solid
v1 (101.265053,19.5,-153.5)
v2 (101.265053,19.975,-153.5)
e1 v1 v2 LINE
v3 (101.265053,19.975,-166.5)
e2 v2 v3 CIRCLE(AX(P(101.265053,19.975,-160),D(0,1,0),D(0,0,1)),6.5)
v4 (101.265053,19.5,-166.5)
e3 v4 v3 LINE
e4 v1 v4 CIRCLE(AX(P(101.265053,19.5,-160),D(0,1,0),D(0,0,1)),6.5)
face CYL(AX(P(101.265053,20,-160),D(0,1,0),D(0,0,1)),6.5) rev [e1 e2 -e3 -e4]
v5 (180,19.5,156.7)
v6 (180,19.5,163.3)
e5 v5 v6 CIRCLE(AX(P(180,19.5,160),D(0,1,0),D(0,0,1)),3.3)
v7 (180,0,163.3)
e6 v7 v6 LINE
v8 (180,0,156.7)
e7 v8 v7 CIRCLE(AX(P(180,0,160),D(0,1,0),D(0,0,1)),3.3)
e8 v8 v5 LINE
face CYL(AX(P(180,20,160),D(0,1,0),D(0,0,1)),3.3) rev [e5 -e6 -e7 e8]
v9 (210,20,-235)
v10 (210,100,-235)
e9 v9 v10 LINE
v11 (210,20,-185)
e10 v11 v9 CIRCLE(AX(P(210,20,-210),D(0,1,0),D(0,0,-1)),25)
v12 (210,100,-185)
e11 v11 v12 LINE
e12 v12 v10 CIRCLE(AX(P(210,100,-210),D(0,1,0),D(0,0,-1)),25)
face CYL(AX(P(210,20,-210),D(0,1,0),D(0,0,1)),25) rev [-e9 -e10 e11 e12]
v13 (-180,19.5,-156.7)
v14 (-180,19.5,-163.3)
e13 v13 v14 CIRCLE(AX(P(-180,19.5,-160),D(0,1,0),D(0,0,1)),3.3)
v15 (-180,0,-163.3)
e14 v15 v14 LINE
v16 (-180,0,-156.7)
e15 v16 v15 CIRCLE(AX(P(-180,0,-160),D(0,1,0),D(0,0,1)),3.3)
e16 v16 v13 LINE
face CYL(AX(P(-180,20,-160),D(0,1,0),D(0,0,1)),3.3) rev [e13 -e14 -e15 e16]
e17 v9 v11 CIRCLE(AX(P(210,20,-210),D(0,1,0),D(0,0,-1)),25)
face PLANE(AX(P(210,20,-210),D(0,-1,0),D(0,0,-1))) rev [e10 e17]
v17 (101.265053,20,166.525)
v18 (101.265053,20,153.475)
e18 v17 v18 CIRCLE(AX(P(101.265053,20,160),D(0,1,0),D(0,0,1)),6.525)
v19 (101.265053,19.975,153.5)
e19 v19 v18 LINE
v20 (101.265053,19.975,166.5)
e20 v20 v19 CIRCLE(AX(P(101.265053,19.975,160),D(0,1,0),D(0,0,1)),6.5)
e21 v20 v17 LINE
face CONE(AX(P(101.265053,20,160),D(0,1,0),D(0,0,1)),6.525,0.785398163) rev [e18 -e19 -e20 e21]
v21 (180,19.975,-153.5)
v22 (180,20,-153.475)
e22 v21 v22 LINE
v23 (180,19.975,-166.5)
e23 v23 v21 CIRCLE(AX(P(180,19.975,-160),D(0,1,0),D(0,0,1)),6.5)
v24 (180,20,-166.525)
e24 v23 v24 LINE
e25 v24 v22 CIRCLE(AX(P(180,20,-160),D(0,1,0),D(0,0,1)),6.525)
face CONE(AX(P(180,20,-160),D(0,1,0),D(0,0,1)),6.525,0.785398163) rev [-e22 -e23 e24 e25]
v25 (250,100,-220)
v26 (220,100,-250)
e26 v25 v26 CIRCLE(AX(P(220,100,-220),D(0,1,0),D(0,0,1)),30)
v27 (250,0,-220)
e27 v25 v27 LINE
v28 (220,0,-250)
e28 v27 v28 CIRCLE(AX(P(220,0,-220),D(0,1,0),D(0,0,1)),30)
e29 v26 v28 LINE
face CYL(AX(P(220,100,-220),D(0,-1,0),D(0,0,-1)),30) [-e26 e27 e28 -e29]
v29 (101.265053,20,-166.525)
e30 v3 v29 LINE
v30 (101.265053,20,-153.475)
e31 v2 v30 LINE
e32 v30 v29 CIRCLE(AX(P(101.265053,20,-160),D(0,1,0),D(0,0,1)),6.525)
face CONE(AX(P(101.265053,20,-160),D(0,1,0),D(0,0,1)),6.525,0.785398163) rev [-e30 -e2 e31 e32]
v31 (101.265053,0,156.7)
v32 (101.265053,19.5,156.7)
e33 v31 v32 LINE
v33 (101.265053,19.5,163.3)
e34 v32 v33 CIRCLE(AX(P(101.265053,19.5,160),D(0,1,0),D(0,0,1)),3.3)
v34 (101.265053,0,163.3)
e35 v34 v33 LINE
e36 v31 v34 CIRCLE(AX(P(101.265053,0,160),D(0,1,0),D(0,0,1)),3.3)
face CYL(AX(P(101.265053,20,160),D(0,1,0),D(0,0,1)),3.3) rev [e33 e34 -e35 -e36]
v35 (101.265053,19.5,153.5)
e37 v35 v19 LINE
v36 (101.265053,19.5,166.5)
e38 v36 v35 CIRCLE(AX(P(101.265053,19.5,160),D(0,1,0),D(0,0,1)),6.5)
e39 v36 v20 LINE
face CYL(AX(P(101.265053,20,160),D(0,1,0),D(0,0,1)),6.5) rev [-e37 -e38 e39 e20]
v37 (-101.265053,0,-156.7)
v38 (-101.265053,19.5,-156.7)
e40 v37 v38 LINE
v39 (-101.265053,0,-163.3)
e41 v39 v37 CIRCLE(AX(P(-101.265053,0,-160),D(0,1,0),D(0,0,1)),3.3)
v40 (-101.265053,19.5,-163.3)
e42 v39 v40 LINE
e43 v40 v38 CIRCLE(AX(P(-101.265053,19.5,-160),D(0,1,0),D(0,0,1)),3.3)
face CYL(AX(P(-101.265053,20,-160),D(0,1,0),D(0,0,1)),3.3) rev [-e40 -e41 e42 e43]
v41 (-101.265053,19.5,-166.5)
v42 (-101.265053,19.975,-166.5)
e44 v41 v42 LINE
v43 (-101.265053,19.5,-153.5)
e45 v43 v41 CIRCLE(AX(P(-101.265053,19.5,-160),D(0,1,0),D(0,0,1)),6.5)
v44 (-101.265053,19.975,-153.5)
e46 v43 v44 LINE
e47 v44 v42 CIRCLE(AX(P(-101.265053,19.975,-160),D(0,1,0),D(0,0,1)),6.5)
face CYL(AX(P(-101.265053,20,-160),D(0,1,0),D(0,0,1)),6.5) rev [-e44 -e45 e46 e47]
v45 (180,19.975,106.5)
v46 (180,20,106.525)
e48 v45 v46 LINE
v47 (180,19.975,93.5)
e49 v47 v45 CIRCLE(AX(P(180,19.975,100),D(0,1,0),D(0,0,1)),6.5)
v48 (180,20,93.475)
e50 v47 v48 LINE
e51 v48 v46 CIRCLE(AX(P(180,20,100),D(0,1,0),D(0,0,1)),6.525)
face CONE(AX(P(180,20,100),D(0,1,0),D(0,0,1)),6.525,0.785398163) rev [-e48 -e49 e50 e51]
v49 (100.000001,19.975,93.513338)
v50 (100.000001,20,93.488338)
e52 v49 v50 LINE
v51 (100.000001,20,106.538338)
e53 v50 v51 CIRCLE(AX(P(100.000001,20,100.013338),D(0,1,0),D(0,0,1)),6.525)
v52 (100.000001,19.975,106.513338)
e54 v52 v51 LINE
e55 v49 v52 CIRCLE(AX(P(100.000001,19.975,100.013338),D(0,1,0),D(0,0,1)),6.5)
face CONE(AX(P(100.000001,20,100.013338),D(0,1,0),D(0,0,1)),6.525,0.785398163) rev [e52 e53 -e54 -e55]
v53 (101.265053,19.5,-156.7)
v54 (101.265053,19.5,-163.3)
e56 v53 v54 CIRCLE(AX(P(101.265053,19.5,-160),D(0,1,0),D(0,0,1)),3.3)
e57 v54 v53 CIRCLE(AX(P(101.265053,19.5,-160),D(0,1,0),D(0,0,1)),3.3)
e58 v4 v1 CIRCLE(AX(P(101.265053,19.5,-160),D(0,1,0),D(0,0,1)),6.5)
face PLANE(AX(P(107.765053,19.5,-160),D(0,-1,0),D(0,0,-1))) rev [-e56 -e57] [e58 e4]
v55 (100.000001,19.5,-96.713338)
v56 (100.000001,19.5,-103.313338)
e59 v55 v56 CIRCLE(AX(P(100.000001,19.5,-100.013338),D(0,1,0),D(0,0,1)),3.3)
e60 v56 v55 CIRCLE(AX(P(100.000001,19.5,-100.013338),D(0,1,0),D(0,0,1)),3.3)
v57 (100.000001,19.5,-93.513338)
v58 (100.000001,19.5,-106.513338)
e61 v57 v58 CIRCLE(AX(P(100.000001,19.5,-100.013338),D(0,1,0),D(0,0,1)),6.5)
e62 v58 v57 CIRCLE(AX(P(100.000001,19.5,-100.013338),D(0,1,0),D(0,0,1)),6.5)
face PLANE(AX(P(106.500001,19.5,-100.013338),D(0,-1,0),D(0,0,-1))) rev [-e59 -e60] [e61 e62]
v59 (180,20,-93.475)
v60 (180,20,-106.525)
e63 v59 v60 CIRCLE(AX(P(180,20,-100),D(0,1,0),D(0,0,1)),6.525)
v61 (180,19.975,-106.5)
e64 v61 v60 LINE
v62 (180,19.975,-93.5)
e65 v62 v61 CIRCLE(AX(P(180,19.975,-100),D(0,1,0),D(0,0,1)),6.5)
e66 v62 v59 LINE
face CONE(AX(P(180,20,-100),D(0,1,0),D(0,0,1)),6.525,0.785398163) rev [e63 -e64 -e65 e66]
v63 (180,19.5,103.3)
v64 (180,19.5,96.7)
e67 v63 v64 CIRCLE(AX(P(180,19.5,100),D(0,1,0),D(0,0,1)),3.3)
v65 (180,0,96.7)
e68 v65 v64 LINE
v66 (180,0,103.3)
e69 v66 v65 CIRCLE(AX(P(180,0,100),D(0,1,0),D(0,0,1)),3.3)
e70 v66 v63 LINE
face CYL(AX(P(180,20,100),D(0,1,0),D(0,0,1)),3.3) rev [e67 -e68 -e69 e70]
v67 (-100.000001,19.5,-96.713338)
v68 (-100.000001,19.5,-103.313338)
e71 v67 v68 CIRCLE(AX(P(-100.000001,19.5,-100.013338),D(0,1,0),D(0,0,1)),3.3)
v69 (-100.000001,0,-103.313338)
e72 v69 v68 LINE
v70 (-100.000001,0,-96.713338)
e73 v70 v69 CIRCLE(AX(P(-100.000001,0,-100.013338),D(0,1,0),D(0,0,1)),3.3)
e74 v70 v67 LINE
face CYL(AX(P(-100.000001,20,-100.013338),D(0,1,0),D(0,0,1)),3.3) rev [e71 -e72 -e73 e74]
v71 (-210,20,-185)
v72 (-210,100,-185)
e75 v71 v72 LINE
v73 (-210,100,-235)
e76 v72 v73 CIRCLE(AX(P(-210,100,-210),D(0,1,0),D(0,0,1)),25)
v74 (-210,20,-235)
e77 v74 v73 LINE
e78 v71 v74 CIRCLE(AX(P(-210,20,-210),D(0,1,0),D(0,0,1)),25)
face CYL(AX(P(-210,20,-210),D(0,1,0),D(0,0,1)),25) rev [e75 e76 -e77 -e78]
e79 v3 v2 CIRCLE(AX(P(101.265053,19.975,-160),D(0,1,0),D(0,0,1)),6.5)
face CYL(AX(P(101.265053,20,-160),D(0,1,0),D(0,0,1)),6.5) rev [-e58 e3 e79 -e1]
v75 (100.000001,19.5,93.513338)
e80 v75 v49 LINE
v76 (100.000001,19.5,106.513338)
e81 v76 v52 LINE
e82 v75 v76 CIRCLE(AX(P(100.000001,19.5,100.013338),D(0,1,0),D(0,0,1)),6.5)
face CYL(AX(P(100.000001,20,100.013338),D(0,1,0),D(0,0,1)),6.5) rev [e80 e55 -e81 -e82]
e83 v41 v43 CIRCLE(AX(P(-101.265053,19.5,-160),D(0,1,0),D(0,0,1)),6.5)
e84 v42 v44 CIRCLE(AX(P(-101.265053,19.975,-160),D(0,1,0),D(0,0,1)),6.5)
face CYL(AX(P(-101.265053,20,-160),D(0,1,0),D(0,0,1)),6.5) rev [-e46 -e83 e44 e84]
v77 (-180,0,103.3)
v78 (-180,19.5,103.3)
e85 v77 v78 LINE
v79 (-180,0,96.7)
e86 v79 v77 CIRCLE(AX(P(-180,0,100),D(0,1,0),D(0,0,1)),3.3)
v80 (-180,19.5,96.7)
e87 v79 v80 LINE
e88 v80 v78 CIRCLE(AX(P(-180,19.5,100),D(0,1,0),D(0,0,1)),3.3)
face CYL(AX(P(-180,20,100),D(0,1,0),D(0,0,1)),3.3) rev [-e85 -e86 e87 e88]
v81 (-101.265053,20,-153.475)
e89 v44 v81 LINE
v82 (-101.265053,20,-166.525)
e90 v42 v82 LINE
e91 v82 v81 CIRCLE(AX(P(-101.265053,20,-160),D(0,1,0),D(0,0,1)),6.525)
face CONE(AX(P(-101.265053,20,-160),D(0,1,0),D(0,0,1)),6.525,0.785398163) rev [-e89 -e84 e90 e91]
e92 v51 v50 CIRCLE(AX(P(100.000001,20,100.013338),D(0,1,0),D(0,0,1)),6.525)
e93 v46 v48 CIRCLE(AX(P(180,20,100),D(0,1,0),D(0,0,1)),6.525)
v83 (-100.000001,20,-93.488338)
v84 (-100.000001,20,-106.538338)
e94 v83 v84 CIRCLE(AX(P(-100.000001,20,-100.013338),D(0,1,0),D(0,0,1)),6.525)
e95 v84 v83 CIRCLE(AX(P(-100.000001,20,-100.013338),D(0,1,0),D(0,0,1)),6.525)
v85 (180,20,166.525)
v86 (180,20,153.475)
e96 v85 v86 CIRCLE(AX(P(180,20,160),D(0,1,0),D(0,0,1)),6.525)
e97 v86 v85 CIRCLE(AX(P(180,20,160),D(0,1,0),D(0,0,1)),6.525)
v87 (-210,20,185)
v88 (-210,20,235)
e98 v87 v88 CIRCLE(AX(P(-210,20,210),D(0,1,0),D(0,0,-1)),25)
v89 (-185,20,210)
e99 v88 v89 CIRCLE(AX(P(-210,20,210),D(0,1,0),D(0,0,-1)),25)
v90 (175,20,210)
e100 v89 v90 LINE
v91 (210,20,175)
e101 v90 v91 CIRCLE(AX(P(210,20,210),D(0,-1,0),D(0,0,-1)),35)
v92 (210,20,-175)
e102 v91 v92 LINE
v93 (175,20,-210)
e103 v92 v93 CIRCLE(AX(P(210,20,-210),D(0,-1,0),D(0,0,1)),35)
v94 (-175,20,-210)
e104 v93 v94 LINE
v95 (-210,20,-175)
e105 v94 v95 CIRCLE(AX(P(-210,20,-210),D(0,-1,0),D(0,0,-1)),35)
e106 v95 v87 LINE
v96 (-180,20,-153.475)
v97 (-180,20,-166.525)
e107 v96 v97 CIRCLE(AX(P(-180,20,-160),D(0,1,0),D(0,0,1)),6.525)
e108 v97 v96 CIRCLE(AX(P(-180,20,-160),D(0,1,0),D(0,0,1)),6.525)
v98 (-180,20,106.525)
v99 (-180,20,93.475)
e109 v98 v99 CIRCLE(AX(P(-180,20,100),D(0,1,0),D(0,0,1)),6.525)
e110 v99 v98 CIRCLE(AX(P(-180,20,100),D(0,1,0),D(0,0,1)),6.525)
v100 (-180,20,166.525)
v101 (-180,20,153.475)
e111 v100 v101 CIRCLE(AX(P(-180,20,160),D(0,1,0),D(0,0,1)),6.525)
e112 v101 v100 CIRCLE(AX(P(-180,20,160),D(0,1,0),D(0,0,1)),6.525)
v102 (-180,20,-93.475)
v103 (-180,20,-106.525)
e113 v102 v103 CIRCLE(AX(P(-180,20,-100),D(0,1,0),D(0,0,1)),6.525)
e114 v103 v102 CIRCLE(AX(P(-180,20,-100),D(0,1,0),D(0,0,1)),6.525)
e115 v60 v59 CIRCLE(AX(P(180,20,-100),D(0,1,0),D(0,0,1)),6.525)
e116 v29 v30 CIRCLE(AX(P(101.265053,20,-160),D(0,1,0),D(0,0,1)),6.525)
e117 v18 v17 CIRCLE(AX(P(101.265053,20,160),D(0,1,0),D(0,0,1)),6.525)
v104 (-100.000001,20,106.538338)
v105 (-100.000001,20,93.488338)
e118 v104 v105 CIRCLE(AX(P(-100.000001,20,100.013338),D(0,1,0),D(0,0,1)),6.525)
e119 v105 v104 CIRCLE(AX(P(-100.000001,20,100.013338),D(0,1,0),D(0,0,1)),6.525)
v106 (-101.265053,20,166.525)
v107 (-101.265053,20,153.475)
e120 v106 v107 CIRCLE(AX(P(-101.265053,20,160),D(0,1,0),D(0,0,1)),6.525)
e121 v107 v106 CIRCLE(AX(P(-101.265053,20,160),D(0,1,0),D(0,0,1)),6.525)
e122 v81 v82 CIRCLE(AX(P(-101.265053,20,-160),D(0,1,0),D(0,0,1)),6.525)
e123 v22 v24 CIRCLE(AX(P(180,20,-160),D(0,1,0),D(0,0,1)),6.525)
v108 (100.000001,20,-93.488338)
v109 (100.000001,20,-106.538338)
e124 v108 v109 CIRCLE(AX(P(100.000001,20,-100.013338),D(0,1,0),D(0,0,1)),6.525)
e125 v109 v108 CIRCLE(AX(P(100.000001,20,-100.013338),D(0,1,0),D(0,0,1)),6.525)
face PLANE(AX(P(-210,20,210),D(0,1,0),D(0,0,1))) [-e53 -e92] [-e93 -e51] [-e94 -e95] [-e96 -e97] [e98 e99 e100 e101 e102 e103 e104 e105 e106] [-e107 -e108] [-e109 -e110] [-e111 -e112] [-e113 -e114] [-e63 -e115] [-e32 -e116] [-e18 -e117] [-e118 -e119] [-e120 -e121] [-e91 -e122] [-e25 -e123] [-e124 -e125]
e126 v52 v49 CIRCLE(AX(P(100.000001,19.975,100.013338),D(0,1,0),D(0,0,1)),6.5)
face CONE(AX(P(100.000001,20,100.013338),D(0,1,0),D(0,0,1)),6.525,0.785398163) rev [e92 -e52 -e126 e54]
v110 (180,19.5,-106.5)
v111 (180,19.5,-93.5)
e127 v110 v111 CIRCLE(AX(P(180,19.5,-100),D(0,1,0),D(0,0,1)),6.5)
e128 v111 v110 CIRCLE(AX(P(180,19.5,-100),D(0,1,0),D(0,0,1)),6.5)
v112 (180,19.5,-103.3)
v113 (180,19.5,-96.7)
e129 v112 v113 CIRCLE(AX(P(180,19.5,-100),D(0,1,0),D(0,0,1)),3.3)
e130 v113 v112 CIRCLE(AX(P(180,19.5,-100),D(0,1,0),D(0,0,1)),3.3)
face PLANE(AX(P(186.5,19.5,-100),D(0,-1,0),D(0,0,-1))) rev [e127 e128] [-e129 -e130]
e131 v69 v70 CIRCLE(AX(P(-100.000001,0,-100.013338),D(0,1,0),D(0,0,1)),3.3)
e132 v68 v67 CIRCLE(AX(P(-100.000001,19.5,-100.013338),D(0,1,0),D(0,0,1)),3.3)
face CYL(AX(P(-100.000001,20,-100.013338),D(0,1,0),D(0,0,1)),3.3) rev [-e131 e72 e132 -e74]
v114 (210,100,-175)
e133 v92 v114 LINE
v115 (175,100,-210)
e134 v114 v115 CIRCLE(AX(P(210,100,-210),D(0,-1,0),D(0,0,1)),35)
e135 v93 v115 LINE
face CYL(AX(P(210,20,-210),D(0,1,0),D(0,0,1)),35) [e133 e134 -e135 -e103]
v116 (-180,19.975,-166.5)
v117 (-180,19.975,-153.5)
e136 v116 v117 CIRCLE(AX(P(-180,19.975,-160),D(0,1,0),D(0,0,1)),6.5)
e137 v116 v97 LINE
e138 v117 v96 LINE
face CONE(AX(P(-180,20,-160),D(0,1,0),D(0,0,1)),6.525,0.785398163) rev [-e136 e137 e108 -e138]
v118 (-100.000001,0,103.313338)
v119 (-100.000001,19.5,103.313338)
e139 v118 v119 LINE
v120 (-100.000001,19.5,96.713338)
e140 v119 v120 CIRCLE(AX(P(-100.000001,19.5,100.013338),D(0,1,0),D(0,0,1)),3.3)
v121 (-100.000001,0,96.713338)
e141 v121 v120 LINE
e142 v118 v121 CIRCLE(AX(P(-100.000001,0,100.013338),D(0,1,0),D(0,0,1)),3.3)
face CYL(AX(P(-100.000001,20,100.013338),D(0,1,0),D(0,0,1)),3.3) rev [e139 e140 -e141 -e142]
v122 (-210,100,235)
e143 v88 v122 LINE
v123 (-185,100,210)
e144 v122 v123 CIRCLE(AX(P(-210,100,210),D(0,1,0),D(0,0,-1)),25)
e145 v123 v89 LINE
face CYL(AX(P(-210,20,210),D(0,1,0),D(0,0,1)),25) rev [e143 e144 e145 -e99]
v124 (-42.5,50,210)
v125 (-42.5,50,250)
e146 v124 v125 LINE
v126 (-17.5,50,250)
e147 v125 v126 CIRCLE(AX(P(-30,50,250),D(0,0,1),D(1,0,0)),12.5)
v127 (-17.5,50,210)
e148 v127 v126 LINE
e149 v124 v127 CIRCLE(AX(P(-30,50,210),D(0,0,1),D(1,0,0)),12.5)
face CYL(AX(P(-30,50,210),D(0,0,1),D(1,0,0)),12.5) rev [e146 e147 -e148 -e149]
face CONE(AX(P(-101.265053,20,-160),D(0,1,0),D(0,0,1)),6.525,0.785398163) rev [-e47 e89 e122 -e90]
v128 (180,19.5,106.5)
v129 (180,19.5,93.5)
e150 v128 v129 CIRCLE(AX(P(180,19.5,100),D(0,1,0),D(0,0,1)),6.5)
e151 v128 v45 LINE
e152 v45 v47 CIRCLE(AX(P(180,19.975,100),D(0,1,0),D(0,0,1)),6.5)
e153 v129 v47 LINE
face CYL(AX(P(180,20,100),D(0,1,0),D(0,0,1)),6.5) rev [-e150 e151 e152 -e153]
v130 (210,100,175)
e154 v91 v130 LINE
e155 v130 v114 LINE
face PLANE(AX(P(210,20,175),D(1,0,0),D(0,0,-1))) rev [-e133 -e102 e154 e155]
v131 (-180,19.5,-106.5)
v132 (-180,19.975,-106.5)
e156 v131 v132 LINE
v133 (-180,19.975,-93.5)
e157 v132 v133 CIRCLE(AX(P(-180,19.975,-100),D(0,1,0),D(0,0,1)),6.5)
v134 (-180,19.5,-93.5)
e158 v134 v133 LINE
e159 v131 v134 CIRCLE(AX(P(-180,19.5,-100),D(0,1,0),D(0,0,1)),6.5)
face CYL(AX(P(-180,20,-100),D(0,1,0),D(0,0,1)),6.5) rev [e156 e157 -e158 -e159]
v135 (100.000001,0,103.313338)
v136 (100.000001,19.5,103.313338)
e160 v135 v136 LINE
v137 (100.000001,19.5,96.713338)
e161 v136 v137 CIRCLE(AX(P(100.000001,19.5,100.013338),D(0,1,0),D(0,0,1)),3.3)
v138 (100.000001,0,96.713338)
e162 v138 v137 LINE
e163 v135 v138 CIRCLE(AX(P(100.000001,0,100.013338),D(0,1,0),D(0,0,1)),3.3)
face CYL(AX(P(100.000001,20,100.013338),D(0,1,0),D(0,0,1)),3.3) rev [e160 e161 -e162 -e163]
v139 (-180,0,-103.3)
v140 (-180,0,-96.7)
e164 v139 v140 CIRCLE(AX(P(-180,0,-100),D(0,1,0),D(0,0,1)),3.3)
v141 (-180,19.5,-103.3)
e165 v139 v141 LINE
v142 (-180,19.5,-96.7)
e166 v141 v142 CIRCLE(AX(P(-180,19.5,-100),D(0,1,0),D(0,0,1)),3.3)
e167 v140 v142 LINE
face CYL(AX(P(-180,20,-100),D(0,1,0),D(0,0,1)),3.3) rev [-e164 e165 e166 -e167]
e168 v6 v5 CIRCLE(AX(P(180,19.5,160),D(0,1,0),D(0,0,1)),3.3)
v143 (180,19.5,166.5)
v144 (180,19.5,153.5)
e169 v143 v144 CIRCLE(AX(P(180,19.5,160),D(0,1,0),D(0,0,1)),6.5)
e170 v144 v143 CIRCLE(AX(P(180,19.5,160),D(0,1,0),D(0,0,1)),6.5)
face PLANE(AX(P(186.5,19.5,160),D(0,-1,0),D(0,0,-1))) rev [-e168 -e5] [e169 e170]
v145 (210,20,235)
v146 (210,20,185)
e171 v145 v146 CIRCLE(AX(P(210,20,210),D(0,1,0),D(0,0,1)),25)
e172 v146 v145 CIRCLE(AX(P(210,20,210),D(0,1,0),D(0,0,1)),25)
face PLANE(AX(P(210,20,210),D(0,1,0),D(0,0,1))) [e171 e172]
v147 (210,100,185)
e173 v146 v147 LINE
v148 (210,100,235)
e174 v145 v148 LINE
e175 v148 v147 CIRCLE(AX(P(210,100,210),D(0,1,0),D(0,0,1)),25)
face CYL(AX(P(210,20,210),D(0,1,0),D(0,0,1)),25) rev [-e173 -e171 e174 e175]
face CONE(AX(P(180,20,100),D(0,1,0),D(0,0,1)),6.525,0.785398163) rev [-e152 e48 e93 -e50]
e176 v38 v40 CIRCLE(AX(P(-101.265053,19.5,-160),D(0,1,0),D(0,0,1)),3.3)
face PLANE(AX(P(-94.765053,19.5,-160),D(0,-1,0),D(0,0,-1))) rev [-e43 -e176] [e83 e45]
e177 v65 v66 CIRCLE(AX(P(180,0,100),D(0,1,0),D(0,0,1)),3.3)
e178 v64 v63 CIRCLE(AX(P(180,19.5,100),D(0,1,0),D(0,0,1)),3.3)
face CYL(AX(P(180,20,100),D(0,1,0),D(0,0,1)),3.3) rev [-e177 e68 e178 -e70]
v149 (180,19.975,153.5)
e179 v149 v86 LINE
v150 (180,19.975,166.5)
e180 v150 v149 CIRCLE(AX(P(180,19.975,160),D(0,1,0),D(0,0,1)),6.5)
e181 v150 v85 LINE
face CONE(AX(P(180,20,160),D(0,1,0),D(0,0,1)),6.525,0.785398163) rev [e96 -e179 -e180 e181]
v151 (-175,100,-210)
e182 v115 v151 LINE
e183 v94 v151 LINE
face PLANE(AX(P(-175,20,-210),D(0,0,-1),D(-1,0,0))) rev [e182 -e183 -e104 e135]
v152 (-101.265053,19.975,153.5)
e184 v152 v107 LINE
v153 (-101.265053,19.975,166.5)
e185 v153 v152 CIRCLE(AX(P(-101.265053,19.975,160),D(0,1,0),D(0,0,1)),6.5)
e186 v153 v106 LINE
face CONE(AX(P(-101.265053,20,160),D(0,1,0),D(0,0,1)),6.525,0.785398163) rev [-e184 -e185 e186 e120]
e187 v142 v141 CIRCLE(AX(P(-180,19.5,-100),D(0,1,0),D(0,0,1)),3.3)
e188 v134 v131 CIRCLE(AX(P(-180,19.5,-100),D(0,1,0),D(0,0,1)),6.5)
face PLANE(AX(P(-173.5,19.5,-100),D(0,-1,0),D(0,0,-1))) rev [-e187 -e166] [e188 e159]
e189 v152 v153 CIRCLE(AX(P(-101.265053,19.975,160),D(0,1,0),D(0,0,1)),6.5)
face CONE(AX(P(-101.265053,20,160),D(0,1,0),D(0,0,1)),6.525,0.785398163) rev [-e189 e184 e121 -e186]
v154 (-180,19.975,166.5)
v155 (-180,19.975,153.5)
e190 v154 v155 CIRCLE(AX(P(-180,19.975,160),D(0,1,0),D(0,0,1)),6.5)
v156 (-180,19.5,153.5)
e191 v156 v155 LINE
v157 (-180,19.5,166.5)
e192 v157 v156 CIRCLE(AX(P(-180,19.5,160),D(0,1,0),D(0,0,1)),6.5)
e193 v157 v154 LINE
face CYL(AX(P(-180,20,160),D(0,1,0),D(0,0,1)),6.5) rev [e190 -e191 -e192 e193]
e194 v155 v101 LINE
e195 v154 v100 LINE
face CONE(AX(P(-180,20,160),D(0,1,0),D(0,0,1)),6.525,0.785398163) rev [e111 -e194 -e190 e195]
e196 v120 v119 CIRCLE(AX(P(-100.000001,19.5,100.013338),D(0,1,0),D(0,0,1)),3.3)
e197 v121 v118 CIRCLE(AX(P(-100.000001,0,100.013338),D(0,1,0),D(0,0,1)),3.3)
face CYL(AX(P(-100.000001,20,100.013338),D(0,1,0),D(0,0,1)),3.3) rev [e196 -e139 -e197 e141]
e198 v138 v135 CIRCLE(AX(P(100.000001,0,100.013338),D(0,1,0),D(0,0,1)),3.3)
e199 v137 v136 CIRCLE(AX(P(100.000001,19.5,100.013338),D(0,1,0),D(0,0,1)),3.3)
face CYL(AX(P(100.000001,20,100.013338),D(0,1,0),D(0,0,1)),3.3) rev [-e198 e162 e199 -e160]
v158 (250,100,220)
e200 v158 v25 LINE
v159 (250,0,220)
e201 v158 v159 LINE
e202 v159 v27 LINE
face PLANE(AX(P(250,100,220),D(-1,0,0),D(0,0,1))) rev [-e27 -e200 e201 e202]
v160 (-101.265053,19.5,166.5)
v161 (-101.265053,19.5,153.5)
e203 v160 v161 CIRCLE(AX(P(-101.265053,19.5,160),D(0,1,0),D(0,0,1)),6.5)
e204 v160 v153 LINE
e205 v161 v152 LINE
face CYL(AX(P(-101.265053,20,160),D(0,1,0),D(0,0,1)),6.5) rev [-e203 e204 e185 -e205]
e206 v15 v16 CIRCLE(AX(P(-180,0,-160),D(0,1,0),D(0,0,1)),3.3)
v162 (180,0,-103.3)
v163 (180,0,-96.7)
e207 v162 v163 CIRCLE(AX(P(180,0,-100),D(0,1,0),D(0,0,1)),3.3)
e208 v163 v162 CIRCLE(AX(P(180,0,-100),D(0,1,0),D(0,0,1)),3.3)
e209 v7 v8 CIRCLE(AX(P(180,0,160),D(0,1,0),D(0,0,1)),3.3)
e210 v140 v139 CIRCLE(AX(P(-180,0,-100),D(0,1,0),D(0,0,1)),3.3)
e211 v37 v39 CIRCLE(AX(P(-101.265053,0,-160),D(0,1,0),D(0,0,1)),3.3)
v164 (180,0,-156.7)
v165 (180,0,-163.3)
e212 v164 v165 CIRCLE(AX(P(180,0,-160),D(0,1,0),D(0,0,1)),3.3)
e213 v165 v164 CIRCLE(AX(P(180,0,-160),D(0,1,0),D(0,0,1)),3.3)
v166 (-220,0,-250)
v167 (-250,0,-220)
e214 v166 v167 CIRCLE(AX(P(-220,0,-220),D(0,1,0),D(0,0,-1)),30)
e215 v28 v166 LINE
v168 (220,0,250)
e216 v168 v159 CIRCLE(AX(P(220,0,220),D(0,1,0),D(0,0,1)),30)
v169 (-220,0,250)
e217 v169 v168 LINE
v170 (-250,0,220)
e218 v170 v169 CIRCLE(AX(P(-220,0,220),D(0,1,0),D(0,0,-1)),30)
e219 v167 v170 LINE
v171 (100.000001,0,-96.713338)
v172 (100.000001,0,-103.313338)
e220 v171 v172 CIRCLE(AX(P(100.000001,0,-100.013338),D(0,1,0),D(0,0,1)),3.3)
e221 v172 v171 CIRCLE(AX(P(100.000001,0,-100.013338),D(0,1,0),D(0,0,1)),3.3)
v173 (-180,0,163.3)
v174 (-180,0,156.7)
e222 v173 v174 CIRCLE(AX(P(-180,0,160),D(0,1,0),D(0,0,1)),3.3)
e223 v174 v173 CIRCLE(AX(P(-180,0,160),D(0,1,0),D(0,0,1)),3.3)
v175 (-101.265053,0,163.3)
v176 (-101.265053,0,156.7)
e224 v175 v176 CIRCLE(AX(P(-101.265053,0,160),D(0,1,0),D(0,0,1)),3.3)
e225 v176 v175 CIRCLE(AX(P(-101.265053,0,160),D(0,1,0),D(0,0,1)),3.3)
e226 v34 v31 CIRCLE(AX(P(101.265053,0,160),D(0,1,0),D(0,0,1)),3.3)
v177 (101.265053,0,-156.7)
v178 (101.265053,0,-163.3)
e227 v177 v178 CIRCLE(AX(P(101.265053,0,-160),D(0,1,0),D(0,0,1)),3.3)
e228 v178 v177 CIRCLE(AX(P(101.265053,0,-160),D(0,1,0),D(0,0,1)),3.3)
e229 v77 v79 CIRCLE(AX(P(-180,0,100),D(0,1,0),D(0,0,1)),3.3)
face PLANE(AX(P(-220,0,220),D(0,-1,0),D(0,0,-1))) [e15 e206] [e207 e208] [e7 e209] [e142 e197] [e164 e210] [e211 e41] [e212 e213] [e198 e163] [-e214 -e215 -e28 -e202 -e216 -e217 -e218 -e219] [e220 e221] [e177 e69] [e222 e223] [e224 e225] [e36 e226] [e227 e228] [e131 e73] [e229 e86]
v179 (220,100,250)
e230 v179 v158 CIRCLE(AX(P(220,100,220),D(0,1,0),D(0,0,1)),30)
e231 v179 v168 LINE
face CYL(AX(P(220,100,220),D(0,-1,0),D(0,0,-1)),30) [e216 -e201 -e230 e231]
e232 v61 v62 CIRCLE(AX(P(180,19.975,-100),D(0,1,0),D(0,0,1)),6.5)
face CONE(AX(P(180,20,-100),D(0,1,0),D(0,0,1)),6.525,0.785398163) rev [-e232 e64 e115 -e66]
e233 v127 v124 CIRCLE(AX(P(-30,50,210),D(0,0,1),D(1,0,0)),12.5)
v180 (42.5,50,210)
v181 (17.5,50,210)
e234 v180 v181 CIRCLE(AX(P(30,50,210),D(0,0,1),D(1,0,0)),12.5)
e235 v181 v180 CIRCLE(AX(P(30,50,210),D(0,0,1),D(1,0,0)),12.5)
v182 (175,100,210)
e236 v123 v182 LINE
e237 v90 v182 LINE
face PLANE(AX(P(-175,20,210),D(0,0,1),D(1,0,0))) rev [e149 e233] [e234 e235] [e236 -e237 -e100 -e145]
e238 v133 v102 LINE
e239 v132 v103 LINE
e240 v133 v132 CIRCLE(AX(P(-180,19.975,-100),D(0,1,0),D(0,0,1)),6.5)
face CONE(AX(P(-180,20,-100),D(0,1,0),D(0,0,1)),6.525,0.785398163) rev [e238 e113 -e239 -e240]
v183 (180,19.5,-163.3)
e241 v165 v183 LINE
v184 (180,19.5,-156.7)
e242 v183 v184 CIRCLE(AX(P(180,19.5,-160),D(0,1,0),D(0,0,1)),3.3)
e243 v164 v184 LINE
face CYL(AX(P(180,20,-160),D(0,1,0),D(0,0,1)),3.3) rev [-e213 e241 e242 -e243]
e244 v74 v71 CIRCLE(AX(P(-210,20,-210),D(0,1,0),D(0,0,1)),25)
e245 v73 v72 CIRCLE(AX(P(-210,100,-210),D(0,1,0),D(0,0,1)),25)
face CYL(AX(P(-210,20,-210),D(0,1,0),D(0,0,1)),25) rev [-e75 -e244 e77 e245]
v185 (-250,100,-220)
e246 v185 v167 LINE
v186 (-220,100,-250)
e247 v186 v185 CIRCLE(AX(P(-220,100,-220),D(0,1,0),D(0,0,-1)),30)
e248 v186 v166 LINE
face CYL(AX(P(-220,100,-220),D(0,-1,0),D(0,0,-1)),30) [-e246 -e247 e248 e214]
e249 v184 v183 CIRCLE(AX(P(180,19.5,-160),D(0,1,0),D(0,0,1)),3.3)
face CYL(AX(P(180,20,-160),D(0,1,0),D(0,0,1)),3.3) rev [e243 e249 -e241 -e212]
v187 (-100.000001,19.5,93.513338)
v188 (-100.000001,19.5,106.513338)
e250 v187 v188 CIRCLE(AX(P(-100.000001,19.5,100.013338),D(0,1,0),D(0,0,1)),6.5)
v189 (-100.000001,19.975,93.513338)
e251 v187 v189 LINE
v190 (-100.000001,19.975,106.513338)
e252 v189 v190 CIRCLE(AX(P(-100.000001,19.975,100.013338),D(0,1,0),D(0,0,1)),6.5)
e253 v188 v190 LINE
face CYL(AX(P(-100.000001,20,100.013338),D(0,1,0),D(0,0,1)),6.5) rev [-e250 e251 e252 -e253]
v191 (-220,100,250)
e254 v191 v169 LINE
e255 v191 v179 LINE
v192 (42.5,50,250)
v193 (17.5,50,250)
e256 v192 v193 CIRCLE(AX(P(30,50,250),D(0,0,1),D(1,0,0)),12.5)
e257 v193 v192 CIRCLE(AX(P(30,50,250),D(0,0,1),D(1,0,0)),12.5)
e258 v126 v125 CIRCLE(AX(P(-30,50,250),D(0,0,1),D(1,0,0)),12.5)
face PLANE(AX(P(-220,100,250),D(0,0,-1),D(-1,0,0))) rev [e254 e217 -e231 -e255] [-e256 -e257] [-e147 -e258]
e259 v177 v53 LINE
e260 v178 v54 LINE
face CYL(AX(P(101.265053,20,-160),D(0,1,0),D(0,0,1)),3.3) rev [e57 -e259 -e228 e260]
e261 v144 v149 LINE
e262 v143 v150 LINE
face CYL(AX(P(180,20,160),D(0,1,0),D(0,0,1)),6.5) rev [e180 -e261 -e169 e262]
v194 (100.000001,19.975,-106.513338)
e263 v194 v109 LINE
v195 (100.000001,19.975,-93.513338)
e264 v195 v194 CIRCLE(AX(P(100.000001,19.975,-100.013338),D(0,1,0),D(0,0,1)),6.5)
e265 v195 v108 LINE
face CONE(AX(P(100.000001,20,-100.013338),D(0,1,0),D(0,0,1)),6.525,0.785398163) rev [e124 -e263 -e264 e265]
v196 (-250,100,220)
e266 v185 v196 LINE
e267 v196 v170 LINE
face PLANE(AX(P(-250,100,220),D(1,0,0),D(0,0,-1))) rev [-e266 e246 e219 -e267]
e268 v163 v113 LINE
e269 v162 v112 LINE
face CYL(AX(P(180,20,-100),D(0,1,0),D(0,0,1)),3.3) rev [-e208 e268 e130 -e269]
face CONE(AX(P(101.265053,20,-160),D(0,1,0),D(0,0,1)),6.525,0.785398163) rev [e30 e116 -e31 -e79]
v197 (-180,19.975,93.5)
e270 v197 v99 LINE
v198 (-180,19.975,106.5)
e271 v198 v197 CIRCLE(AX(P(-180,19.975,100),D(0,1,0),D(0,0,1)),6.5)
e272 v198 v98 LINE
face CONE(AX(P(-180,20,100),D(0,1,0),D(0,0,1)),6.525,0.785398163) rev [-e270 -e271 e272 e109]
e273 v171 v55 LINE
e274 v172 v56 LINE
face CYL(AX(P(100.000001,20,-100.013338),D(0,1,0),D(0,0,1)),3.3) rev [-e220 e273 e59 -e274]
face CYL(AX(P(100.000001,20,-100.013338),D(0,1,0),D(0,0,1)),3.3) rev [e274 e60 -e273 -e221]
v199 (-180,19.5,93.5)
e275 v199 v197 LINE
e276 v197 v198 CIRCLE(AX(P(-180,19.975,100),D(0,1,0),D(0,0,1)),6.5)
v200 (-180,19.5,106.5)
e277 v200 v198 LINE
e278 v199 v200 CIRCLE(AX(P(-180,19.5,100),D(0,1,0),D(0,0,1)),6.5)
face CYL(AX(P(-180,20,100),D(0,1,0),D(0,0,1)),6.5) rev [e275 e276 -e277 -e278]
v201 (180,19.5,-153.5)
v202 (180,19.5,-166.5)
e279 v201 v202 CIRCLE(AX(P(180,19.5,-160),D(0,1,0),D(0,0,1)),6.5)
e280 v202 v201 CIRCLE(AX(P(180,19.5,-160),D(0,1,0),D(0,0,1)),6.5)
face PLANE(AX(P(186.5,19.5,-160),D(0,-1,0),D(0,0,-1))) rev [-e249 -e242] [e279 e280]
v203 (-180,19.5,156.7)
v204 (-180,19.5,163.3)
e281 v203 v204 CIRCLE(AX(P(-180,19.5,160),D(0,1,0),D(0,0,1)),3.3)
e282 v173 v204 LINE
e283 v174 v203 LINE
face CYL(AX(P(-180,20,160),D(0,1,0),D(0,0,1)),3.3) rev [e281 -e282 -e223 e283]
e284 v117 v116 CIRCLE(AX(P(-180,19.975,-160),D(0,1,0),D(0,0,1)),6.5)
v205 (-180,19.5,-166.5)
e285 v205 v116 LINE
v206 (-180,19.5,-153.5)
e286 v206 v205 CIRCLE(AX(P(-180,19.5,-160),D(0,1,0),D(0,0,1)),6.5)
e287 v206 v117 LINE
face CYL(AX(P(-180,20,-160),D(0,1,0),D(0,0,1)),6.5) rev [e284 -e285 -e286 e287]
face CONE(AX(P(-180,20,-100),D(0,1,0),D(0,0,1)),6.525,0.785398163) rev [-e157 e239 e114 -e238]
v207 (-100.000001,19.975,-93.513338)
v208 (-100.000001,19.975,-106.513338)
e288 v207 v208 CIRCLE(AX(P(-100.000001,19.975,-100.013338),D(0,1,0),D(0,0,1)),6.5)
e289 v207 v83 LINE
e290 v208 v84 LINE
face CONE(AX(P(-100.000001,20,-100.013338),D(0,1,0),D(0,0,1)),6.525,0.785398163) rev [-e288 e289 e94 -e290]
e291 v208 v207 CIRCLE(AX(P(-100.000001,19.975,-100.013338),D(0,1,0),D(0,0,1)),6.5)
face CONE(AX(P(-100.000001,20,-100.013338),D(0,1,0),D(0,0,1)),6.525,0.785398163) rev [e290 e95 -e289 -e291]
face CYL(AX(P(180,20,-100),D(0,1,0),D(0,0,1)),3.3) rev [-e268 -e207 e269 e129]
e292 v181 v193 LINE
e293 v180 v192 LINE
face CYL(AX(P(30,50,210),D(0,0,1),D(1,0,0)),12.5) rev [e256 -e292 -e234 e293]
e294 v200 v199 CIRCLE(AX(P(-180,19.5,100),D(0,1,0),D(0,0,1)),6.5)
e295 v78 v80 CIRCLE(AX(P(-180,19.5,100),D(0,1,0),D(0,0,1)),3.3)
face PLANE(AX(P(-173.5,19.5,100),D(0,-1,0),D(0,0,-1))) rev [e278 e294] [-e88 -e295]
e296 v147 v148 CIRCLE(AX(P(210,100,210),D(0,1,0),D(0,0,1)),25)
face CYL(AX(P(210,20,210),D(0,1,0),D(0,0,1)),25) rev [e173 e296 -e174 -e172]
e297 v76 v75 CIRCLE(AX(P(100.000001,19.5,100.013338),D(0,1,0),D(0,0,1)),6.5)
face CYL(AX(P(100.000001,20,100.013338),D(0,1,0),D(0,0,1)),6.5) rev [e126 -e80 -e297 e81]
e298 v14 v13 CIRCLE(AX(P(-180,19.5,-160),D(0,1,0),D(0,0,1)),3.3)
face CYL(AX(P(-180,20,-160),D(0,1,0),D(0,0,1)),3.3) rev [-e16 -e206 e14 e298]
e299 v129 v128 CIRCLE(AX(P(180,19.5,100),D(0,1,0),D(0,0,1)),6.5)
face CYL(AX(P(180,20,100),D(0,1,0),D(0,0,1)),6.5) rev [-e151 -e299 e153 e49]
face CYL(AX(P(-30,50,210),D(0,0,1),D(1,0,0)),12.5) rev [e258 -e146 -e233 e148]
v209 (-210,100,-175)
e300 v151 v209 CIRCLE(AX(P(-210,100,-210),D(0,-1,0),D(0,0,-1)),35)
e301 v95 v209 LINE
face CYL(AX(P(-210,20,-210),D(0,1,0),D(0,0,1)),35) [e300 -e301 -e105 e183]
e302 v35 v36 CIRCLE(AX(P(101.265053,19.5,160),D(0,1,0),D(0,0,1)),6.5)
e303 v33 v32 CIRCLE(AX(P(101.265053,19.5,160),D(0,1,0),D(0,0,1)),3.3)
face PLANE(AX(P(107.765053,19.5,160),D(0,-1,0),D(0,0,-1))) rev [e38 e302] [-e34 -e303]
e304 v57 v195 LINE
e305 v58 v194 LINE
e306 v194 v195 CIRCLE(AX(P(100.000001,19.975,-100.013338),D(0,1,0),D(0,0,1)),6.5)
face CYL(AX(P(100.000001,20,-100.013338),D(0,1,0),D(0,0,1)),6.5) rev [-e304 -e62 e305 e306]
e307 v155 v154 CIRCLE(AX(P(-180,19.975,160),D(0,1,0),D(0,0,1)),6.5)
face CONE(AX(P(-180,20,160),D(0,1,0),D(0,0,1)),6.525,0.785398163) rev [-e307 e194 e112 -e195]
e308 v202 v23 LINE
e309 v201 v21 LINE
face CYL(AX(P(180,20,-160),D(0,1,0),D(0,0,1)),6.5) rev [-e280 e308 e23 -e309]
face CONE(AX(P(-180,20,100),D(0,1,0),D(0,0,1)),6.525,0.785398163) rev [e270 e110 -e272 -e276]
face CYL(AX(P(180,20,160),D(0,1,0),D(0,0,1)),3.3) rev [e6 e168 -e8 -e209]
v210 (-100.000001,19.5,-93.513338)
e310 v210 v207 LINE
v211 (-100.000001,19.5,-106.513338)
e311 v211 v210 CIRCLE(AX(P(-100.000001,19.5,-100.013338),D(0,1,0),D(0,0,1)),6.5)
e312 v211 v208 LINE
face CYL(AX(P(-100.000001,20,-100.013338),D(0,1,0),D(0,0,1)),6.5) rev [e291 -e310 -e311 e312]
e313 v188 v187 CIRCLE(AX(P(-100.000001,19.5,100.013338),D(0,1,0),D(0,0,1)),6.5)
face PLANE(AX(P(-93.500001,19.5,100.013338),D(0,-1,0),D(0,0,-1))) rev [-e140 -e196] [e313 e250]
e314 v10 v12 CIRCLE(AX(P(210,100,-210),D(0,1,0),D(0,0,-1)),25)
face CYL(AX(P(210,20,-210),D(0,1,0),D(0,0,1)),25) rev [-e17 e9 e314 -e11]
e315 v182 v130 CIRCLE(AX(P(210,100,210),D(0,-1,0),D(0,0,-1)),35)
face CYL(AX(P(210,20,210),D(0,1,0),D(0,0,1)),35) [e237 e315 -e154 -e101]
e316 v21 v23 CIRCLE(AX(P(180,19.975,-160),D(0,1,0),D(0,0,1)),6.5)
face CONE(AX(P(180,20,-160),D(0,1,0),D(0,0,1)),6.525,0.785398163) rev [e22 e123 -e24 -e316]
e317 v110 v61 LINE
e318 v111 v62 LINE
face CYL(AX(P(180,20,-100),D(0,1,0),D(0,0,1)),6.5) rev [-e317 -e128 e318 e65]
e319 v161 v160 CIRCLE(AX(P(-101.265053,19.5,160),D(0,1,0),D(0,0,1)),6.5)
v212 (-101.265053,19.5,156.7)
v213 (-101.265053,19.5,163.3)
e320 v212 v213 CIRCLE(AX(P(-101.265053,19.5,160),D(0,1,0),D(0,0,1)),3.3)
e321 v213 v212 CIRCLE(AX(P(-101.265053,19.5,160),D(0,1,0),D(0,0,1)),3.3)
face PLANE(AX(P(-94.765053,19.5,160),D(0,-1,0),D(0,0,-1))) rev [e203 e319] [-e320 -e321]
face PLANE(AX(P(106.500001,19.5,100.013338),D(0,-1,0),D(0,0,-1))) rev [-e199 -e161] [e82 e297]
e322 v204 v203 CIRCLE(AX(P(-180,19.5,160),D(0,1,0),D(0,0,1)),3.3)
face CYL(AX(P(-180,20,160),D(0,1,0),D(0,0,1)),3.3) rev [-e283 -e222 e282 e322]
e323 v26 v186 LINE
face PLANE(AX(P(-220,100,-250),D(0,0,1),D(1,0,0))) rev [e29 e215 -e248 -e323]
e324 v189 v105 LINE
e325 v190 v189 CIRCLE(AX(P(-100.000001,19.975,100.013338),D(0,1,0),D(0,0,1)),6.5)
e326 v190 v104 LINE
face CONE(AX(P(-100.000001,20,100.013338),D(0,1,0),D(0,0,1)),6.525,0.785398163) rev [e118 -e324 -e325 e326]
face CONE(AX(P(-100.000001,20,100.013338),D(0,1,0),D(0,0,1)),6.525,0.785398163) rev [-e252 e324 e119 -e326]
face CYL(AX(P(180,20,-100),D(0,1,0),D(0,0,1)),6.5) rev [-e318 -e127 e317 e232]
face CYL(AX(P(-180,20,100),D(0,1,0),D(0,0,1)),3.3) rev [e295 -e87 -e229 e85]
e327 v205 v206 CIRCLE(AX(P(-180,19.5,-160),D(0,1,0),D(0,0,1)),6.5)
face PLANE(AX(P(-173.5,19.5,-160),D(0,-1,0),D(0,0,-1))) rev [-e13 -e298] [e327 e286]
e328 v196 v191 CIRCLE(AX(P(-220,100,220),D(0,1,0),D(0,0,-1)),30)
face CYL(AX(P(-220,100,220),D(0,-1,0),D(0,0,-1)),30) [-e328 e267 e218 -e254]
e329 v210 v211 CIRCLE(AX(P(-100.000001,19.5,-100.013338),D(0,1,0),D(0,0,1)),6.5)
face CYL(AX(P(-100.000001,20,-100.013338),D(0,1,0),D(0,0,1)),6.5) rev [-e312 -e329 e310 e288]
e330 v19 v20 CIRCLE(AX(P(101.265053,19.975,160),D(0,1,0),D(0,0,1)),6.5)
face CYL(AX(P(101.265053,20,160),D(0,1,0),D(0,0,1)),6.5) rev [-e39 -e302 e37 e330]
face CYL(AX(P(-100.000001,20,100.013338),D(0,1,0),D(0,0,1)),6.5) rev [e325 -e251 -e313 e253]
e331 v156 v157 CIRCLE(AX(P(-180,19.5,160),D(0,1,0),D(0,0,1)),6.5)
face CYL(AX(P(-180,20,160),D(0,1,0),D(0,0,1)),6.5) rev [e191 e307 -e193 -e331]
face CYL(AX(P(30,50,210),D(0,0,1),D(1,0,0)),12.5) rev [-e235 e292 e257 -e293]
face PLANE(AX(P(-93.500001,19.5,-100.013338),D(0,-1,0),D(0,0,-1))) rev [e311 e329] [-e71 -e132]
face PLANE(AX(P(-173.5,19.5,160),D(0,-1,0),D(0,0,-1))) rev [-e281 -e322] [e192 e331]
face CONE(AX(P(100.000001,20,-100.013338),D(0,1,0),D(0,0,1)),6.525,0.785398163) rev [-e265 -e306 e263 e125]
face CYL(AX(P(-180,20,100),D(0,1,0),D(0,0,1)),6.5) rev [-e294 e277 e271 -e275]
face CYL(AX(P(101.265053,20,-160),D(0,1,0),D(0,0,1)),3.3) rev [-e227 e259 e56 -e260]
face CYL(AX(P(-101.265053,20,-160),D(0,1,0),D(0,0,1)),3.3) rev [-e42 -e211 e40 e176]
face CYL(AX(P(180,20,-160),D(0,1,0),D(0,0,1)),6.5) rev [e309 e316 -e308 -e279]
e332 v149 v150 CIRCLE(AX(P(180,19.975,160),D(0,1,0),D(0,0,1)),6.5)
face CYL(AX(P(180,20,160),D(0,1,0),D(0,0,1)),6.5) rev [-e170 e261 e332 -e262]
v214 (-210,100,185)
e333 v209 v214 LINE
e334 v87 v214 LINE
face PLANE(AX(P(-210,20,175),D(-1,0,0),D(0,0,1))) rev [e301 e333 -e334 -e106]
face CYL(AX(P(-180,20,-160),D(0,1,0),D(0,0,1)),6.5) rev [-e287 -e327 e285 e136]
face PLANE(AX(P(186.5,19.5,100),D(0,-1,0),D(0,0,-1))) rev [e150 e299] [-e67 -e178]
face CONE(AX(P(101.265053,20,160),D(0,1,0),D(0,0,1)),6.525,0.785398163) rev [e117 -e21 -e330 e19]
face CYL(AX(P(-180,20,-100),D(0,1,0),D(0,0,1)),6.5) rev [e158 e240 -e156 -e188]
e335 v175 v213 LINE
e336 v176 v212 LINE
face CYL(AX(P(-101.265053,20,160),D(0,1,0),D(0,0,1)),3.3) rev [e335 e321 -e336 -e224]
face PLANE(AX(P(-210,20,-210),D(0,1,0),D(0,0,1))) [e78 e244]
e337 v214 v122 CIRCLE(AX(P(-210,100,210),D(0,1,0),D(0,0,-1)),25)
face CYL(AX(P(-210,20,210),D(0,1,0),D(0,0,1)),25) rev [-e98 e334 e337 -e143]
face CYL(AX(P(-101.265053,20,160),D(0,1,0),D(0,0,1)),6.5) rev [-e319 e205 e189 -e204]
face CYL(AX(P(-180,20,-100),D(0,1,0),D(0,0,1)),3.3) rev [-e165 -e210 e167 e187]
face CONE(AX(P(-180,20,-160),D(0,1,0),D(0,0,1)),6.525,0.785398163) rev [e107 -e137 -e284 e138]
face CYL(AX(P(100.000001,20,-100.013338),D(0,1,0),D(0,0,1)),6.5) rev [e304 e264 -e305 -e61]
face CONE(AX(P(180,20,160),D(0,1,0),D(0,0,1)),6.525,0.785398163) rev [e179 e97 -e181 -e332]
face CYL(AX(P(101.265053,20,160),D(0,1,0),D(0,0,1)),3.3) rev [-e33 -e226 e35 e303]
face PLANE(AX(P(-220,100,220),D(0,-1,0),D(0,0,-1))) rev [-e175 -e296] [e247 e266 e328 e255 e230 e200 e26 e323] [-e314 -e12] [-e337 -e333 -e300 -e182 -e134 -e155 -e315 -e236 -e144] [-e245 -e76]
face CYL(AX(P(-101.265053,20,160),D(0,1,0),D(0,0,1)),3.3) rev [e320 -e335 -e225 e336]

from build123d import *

# Parameters (mm, degrees)
BOSS_EXTRUDE1_DEPTH                          = 100
CUT_EXTRUDE1_DEPTH                           = 80
SKETCH3_R                                    = 25
CUT_EXTRUDE2_DEPTH                           = 80
SKETCH10_R                                   = 12.5
CUT_EXTRUDE4_DEPTH                           = 40
CBORE_FOR_M6_HEXAGON_HEAD_BOLTS_FULL_2_COUNT = 2
CBORE_FOR_M6_HEXAGON_HEAD_BOLTS_FULL_2_PITCH = 80
CBORE_FOR_M6_HEXAGON_HEAD_BOLTS_FULL_3_COUNT = 2
CBORE_FOR_M6_HEXAGON_HEAD_BOLTS_FULL_3_PITCH = 60
CBORE_FOR_M6_HEXAGON_HEAD_BOLTS_FULL_4_COUNT = 2
CBORE_FOR_M6_HEXAGON_HEAD_BOLTS_FULL_4_PITCH = 98.990867508
CUT_EXTRUDE5_DEPTH                           = 80


with BuildPart() as part:
    # Sketch1 → Boss-Extrude1 (new body)
    with BuildSketch(Plane(origin=(0, 0, 0), x_dir=(1, 0, 0), z_dir=(0, 1, 0))):
        with BuildLine():
            Line((-220, -250), (220, -250))
            ThreePointArc((220, -250), (241.213203436, -241.213203436), (250, -220))
            Line((250, -220), (250, 220))
            ThreePointArc((250, 220), (241.213203436, 241.213203436), (220, 250))
            Line((220, 250), (-220, 250))
            ThreePointArc((-220, 250), (-241.213203436, 241.213203436), (-250, 220))
            Line((-250, 220), (-250, -220))
            ThreePointArc((-250, -220), (-241.213203436, -241.213203436), (-220, -250))
        make_face()
    extrude(amount=BOSS_EXTRUDE1_DEPTH)

    # Sketch2 → Cut-Extrude1 (cut)
    with BuildSketch(Plane(origin=(0, 100, 0), x_dir=(1, 0, 0), z_dir=(0, 1, 0))):
        with BuildLine():
            Line((-175, -210), (175, -210))
            ThreePointArc((175, -210), (185.251262658, -185.251262658), (210, -175))
            Line((210, -175), (210, 175))
            ThreePointArc((210, 175), (185.251262658, 185.251262658), (175, 210))
            Line((175, 210), (-175, 210))
            ThreePointArc((-175, 210), (-185.251262658, 185.251262658), (-210, 175))
            Line((-210, 175), (-210, -175))
            ThreePointArc((-210, -175), (-185.251262658, -185.251262658), (-175, -210))
        make_face()
    extrude(amount=-CUT_EXTRUDE1_DEPTH, mode=Mode.SUBTRACT)

    # Sketch3 → Cut-Extrude2 (cut)
    with BuildSketch(Plane(origin=(0, 100, 0), x_dir=(1, 0, 0), z_dir=(0, 1, 0))):
        with Locations(Location((-210, 210, 0), (0, 0, 270))):
            Circle(SKETCH3_R)
        with Locations(Location((210, 210, 0), (0, 0, 90))):
            Circle(SKETCH3_R)
        with Locations(Location((210, -210, 0), (0, 0, 270))):
            Circle(SKETCH3_R)
        with Locations(Location((-210, -210, 0), (0, 0, 90))):
            Circle(SKETCH3_R)
    extrude(amount=-CUT_EXTRUDE2_DEPTH, mode=Mode.SUBTRACT)

    # Sketch10 → Cut-Extrude4 (cut)
    with BuildSketch(Plane.XY.offset(250)):
        with Locations((-30, 50)):
            Circle(SKETCH10_R)
        with Locations((30, 50)):
            Circle(SKETCH10_R)
    extrude(amount=-CUT_EXTRUDE4_DEPTH, mode=Mode.SUBTRACT)

    # Sketch12 → CBORE for M6 Hexagon head bolts-Full thread-grade C1 (revolve, cut)
    with BuildSketch(Plane(origin=(-180, 20, 100), x_dir=(0, 0, 1), z_dir=(1, 0, 0))):
        Polygon((0, 0), (0, 20), (3.3, 20), (3.3, 0.5), (6.5, 0.5), (6.5, 0.025), (6.525, 0), align=None)
    cbore_for_m6_hexagon_head_bolts_full_thr = revolve(axis=Axis((-180, 26.35, 100), (0, -1, 0)), mode=Mode.SUBTRACT)

    # CBORE for M6 Hexagon head bolts-Full 2: CBORE for M6 Hexagon head bolts-Full thread-grade C1 ×2
    with Locations(*[Vector(0.9999999861018275, 0, 0.0001667223586748534) * (i * CBORE_FOR_M6_HEXAGON_HEAD_BOLTS_FULL_2_PITCH) for i in range(1, CBORE_FOR_M6_HEXAGON_HEAD_BOLTS_FULL_2_COUNT)]):
        add(cbore_for_m6_hexagon_head_bolts_full_thr, mode=Mode.SUBTRACT)

    # CBORE for M6 Hexagon head bolts-Full 3: CBORE for M6 Hexagon head bolts-Full thread-grade C1 ×2
    with Locations(*[(0, 0, i * CBORE_FOR_M6_HEXAGON_HEAD_BOLTS_FULL_3_PITCH) for i in range(1, CBORE_FOR_M6_HEXAGON_HEAD_BOLTS_FULL_3_COUNT)]):
        add(cbore_for_m6_hexagon_head_bolts_full_thr, mode=Mode.SUBTRACT)

    # CBORE for M6 Hexagon head bolts-Full 4: CBORE for M6 Hexagon head bolts-Full thread-grade C1 ×2
    with Locations(*[Vector(0.795375864434165, 0, 0.6061165187285402) * (i * CBORE_FOR_M6_HEXAGON_HEAD_BOLTS_FULL_4_PITCH) for i in range(1, CBORE_FOR_M6_HEXAGON_HEAD_BOLTS_FULL_4_COUNT)]):
        add(cbore_for_m6_hexagon_head_bolts_full_thr, mode=Mode.SUBTRACT)

    # Mirror1: CBORE for M6 Hexagon head bolts-Full thread-grade C1 across plane
    add(cbore_for_m6_hexagon_head_bolts_full_thr.mirror(Plane.XY), mode=Mode.SUBTRACT)

    # Mirror1 copy 1 sketch → Mirror1 copy 1 (revolve, cut)
    with BuildSketch(Plane(origin=(-100.000001112, 20, -100.013337789), x_dir=(0, 0, -1), z_dir=(1, 0, 0))):
        Polygon((0, 0), (0, -20), (3.3, -20), (3.3, -0.5), (6.5, -0.5), (6.5, -0.025), (6.525, 0), align=None)
    revolve(axis=Axis((-100.000001112, 26.35, -100.013337789), (0, 1, 0)), mode=Mode.SUBTRACT)

    # Mirror1 copy 2 sketch → Mirror1 copy 2 (revolve, cut)
    with BuildSketch(Plane(origin=(-180, 20, -160), x_dir=(0, 0, -1), z_dir=(1, 0, 0))):
        Polygon((0, 0), (0, -20), (3.3, -20), (3.3, -0.5), (6.5, -0.5), (6.5, -0.025), (6.525, 0), align=None)
    revolve(axis=Axis((-180, 26.35, -160), (0, 1, 0)), mode=Mode.SUBTRACT)

    # Mirror1 copy 3 sketch → Mirror1 copy 3 (revolve, cut)
    with BuildSketch(Plane(origin=(-101.265053185, 20, -160), x_dir=(0, 0, -1), z_dir=(1, 0, 0))):
        Polygon((0, 0), (0, -20), (3.3, -20), (3.3, -0.5), (6.5, -0.5), (6.5, -0.025), (6.525, 0), align=None)
    revolve(axis=Axis((-101.265053185, 26.35, -160), (0, 1, 0)), mode=Mode.SUBTRACT)

    # Mirror1 at the second plane: CBORE for M6 Hexagon head bolts-Full thread-grade C1 across plane
    add(cbore_for_m6_hexagon_head_bolts_full_thr.mirror(Plane(origin=(0, 0, 0), x_dir=(0, 0, 1), z_dir=(1, 0, 0))), mode=Mode.SUBTRACT)

    # Mirror1 at the second plane copy 1 sketc → Mirror1 at the second plane copy 1 (revolve, cut)
    with BuildSketch(Plane(origin=(100.000001112, 20, 100.013337789), x_dir=(0, 0, 1), z_dir=(-1, 0, 0))):
        Polygon((0, 0), (0, -20), (3.3, -20), (3.3, -0.5), (6.5, -0.5), (6.5, -0.025), (6.525, 0), align=None)
    revolve(axis=Axis((100.000001112, 26.35, 100.013337789), (0, 1, 0)), mode=Mode.SUBTRACT)

    # Mirror1 at the second plane copy 2 sketc → Mirror1 at the second plane copy 2 (revolve, cut)
    with BuildSketch(Plane(origin=(180, 20, 160), x_dir=(0, 0, 1), z_dir=(-1, 0, 0))):
        Polygon((0, 0), (0, -20), (3.3, -20), (3.3, -0.5), (6.5, -0.5), (6.5, -0.025), (6.525, 0), align=None)
    revolve(axis=Axis((180, 26.35, 160), (0, 1, 0)), mode=Mode.SUBTRACT)

    # Mirror1 at the second plane copy 3 sketc → Mirror1 at the second plane copy 3 (revolve, cut)
    with BuildSketch(Plane(origin=(101.265053185, 20, 160), x_dir=(0, 0, 1), z_dir=(-1, 0, 0))):
        Polygon((0, 0), (0, -20), (3.3, -20), (3.3, -0.5), (6.5, -0.5), (6.5, -0.025), (6.525, 0), align=None)
    revolve(axis=Axis((101.265053185, 26.35, 160), (0, 1, 0)), mode=Mode.SUBTRACT)

    # Mirror1 at the second plane copy 4 sketc → Mirror1 at the second plane copy 4 (revolve, cut)
    with BuildSketch(Plane(origin=(180, 20, -100), x_dir=(0, 0, -1), z_dir=(-1, 0, 0))):
        Polygon((0, 0), (0, 20), (3.3, 20), (3.3, 0.5), (6.5, 0.5), (6.5, 0.025), (6.525, 0), align=None)
    revolve(axis=Axis((180, 26.35, -100), (0, -1, 0)), mode=Mode.SUBTRACT)

    # Mirror1 at the second plane copy 5 sketc → Mirror1 at the second plane copy 5 (revolve, cut)
    with BuildSketch(Plane(origin=(100.000001112, 20, -100.013337789), x_dir=(0, 0, -1), z_dir=(-1, 0, 0))):
        Polygon((0, 0), (0, 20), (3.3, 20), (3.3, 0.5), (6.5, 0.5), (6.5, 0.025), (6.525, 0), align=None)
    revolve(axis=Axis((100.000001112, 26.35, -100.013337789), (0, -1, 0)), mode=Mode.SUBTRACT)

    # Mirror1 at the second plane copy 6 sketc → Mirror1 at the second plane copy 6 (revolve, cut)
    with BuildSketch(Plane(origin=(180, 20, -160), x_dir=(0, 0, -1), z_dir=(-1, 0, 0))):
        Polygon((0, 0), (0, 20), (3.3, 20), (3.3, 0.5), (6.5, 0.5), (6.5, 0.025), (6.525, 0), align=None)
    revolve(axis=Axis((180, 26.35, -160), (0, -1, 0)), mode=Mode.SUBTRACT)

    # Mirror1 at the second plane copy 7 sketc → Mirror1 at the second plane copy 7 (revolve, cut)
    with BuildSketch(Plane(origin=(101.265053185, 20, -160), x_dir=(0, 0, -1), z_dir=(-1, 0, 0))):
        Polygon((0, 0), (0, 20), (3.3, 20), (3.3, 0.5), (6.5, 0.5), (6.5, 0.025), (6.525, 0), align=None)
    revolve(axis=Axis((101.265053185, 26.35, -160), (0, -1, 0)), mode=Mode.SUBTRACT)

    # Sketch14 → Cut-Extrude5 (cut)
    with BuildSketch(Plane(origin=(0, 100, 0), x_dir=(1, 0, 0), z_dir=(0, 1, 0))):
        with BuildLine():
            Line((-210, -175), (-210, -210))
            Line((-210, -210), (-175, -210))
            ThreePointArc((-175, -210), (-185.251262658, -185.251262658), (-210, -175))
        make_face()
    extrude(amount=-CUT_EXTRUDE5_DEPTH, mode=Mode.SUBTRACT)


solid = part.part
